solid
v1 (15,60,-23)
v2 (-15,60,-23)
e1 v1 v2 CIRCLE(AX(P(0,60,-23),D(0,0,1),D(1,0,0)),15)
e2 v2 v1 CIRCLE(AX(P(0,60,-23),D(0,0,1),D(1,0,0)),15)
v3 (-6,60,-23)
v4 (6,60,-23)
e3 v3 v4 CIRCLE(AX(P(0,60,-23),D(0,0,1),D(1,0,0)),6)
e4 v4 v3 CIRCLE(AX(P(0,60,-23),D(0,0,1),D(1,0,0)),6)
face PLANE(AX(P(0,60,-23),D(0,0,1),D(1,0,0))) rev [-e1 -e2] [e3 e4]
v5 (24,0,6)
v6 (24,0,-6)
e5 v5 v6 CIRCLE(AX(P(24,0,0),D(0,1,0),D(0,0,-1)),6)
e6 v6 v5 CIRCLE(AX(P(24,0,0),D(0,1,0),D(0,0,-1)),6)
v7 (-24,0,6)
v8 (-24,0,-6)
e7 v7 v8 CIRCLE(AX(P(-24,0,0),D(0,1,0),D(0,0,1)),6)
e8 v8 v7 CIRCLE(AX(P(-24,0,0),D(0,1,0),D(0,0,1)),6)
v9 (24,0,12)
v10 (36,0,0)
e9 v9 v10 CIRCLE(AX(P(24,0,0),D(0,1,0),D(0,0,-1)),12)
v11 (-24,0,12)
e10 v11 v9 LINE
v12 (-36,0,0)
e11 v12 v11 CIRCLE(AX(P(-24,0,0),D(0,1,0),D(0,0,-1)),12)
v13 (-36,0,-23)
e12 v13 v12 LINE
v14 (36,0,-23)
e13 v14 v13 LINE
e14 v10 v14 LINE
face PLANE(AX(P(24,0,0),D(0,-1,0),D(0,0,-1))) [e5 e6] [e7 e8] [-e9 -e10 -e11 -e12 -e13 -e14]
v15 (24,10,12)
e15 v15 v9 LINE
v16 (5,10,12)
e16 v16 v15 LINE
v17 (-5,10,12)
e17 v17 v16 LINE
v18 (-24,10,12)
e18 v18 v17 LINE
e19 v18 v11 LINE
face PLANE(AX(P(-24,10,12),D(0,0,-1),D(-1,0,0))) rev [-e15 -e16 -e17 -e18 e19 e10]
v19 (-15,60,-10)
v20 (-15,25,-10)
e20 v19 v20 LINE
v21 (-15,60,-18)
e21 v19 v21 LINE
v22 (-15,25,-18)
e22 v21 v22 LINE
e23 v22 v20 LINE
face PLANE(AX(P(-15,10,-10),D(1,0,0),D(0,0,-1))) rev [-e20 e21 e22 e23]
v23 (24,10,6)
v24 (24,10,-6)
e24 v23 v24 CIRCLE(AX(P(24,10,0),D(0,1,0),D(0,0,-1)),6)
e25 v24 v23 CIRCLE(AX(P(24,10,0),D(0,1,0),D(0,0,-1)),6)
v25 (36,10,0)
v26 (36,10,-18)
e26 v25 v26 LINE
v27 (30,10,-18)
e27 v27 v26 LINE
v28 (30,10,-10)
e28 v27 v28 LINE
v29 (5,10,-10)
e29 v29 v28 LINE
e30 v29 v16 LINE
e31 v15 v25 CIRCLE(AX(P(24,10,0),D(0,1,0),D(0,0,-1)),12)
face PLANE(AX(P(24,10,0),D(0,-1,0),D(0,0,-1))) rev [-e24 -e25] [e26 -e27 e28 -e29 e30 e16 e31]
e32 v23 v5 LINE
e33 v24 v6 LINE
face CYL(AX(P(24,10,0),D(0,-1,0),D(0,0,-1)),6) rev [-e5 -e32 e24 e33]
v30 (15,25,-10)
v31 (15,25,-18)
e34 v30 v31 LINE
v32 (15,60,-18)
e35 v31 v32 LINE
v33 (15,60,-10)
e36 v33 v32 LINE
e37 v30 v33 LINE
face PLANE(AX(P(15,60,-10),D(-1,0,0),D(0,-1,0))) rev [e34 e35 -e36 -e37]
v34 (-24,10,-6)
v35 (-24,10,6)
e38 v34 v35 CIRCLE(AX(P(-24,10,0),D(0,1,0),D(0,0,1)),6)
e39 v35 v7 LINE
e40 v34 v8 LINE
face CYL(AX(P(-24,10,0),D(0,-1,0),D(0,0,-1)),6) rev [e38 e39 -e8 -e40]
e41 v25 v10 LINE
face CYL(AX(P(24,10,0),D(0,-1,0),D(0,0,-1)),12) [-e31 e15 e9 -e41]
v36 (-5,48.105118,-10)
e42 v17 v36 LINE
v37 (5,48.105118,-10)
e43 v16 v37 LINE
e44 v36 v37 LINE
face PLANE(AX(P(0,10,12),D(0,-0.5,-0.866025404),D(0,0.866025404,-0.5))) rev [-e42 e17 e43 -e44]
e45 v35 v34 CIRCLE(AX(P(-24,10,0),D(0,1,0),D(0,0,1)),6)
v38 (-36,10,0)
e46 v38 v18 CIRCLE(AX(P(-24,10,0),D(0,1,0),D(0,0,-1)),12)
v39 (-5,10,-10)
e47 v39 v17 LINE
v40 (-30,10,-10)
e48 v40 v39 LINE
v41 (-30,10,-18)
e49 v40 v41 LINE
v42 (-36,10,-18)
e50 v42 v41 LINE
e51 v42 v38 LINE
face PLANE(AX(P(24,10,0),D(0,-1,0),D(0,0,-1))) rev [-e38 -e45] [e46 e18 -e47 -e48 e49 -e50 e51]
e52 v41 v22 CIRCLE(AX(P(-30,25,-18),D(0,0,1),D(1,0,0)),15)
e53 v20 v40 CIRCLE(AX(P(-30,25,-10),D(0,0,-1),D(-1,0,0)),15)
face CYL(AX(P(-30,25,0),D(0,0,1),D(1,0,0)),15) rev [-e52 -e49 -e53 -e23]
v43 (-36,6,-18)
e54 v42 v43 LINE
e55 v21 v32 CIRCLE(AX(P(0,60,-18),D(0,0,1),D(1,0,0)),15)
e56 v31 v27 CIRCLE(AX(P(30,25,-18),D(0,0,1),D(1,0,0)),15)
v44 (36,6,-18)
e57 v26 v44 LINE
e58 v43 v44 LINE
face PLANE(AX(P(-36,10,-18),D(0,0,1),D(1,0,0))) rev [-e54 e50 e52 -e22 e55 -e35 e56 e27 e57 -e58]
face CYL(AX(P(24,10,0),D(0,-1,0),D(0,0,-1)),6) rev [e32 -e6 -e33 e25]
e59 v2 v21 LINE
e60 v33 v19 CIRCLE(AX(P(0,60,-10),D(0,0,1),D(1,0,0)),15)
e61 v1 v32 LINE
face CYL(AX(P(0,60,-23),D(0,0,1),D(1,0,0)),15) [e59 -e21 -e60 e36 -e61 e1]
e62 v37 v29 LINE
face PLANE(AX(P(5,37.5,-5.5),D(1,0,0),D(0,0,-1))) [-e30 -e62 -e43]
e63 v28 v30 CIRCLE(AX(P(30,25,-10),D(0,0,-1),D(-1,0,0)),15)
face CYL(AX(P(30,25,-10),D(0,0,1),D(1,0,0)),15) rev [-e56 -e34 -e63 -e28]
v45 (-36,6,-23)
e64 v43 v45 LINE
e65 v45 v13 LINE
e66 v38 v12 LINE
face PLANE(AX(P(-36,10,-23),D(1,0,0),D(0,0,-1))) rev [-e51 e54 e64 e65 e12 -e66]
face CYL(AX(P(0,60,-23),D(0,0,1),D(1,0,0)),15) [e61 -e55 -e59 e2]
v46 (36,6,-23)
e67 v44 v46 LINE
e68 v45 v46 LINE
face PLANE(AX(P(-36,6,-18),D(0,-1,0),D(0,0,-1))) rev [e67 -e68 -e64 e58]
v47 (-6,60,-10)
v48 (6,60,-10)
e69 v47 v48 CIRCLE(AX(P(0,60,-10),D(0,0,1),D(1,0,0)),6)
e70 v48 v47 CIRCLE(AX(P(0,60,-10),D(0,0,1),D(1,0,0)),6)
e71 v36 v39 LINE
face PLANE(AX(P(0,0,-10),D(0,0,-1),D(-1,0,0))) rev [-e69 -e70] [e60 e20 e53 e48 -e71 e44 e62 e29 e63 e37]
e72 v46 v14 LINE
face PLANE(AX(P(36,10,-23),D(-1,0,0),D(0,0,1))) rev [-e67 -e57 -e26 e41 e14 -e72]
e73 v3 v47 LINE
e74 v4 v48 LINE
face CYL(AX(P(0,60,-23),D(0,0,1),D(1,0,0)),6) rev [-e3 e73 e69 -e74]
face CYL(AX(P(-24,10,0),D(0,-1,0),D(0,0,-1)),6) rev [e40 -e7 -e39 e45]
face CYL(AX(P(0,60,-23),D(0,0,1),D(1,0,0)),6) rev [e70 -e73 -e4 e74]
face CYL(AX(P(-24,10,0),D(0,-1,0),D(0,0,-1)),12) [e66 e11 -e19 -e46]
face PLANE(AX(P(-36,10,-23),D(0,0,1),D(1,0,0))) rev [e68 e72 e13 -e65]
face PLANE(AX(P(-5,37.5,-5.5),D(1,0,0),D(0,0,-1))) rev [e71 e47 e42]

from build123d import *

# Parameters (mm, degrees)
BASE_PLATE_SKETCH_R       = 6
BASE_PLATE_DEPTH          = 10
REAR_GROOVE_SKETCH_W      = 5
REAR_GROOVE_SKETCH_H      = 4
REAR_GROOVE_4X5_DEPTH     = 77.243032469
UPRIGHT_SKETCH_W          = 30
UPRIGHT_SKETCH_H          = 50
UPRIGHT_DEPTH             = 8
HUB_BOSS_SKETCH_R         = 15
HUB_BOSS_SKETCH_R_2       = 6
HUB_BOSS_DEPTH            = 13
SHAFT_START               = -13
SHAFT_BORE_SKETCH_R       = 6
SHAFT_BORE_DEPTH          = 13
UPRIGHT_BASE_FILLET_R15_R = 15
SUPPORT_RIB_REACH         = 88.313
SUPPORT_RIB_SKETCH_WALL_W = 218.626765016
SUPPORT_RIB_SKETCH_WALL_H = 10


with BuildPart() as part:
    # Base Plate Sketch → Base Plate (new body)
    with BuildSketch(Plane(origin=(0, 0, 0), x_dir=(1, 0, 0), z_dir=(0, 1, 0))):
        with BuildLine():
            Line((-36, 23), (-36, 0))
            ThreePointArc((-36, 0), (-32.485281374, -8.485281374), (-24, -12))
            Line((-24, -12), (24, -12))
            ThreePointArc((24, -12), (32.485281374, -8.485281374), (36, 0))
            Line((36, 0), (36, 23))
            Line((36, 23), (-36, 23))
        make_face()
        with Locations(Location((-24, 0, 0), (0, 0, 270))):
            Circle(BASE_PLATE_SKETCH_R, mode=Mode.SUBTRACT)
        with Locations(Location((24, 0, 0), (0, 0, 90))):
            Circle(BASE_PLATE_SKETCH_R, mode=Mode.SUBTRACT)
    extrude(amount=BASE_PLATE_DEPTH)

    # Rear Groove Sketch → Rear Groove 4x5 (cut, through all)
    with BuildSketch(Plane(origin=(36, 0, 0), x_dir=(0, 0, -1), z_dir=(1, 0, 0))):
        with Locations((20.5, 8)):
            Rectangle(REAR_GROOVE_SKETCH_W, REAR_GROOVE_SKETCH_H)
    extrude(amount=-REAR_GROOVE_4X5_DEPTH, mode=Mode.SUBTRACT)

    # Upright Sketch → Upright (add)
    with BuildSketch(Plane.XY.offset(-18)):
        with Locations((0, 35)):
            Rectangle(UPRIGHT_SKETCH_W, UPRIGHT_SKETCH_H)
    extrude(amount=UPRIGHT_DEPTH)

    # Hub Boss Sketch → Hub Boss (add)
    with BuildSketch(Plane.XY.offset(-10)):
        with Locations((0, 60)):
            Circle(HUB_BOSS_SKETCH_R)
        with Locations((0, 60)):
            Circle(HUB_BOSS_SKETCH_R_2, mode=Mode.SUBTRACT)
    extrude(amount=-HUB_BOSS_DEPTH)

    # Shaft Bore Sketch → Shaft Bore (cut)
    with BuildSketch(Plane(origin=(0, 0, -23), x_dir=(-1, 0, 0), z_dir=(0, 0, -1)).offset(SHAFT_START)):
        with Locations(Location((0, 60, 0), (0, 0, 180))):
            Circle(SHAFT_BORE_SKETCH_R)
    extrude(amount=SHAFT_BORE_DEPTH, mode=Mode.SUBTRACT)

    # Upright Base Fillet R15
    upright_base_fillet_r15_edges = [part.edges().sort_by_distance(p)[0] for p in [
        (-15, 10, -14),
        (15, 10, -14),
    ]]
    fillet(upright_base_fillet_r15_edges, radius=UPRIGHT_BASE_FILLET_R15_R)

    # Support Rib Sketch wall → Support Rib (add, up to next)
    with BuildSketch(Plane(origin=(0, 29.052558884, 1), x_dir=(0, 0.866025403787, -0.499999999995), z_dir=(0, 0.499999999995, 0.866025403787)), mode=Mode.PRIVATE) as support_rib_sk1:
        Rectangle(SUPPORT_RIB_SKETCH_WALL_W, SUPPORT_RIB_SKETCH_WALL_H)
    support_rib_tool1 = extrude(support_rib_sk1.sketch, amount=-SUPPORT_RIB_REACH, mode=Mode.PRIVATE) - part.part
    add(support_rib_tool1.solids().sort_by_distance((0, 29.052558884, 1))[0])


solid = part.part
